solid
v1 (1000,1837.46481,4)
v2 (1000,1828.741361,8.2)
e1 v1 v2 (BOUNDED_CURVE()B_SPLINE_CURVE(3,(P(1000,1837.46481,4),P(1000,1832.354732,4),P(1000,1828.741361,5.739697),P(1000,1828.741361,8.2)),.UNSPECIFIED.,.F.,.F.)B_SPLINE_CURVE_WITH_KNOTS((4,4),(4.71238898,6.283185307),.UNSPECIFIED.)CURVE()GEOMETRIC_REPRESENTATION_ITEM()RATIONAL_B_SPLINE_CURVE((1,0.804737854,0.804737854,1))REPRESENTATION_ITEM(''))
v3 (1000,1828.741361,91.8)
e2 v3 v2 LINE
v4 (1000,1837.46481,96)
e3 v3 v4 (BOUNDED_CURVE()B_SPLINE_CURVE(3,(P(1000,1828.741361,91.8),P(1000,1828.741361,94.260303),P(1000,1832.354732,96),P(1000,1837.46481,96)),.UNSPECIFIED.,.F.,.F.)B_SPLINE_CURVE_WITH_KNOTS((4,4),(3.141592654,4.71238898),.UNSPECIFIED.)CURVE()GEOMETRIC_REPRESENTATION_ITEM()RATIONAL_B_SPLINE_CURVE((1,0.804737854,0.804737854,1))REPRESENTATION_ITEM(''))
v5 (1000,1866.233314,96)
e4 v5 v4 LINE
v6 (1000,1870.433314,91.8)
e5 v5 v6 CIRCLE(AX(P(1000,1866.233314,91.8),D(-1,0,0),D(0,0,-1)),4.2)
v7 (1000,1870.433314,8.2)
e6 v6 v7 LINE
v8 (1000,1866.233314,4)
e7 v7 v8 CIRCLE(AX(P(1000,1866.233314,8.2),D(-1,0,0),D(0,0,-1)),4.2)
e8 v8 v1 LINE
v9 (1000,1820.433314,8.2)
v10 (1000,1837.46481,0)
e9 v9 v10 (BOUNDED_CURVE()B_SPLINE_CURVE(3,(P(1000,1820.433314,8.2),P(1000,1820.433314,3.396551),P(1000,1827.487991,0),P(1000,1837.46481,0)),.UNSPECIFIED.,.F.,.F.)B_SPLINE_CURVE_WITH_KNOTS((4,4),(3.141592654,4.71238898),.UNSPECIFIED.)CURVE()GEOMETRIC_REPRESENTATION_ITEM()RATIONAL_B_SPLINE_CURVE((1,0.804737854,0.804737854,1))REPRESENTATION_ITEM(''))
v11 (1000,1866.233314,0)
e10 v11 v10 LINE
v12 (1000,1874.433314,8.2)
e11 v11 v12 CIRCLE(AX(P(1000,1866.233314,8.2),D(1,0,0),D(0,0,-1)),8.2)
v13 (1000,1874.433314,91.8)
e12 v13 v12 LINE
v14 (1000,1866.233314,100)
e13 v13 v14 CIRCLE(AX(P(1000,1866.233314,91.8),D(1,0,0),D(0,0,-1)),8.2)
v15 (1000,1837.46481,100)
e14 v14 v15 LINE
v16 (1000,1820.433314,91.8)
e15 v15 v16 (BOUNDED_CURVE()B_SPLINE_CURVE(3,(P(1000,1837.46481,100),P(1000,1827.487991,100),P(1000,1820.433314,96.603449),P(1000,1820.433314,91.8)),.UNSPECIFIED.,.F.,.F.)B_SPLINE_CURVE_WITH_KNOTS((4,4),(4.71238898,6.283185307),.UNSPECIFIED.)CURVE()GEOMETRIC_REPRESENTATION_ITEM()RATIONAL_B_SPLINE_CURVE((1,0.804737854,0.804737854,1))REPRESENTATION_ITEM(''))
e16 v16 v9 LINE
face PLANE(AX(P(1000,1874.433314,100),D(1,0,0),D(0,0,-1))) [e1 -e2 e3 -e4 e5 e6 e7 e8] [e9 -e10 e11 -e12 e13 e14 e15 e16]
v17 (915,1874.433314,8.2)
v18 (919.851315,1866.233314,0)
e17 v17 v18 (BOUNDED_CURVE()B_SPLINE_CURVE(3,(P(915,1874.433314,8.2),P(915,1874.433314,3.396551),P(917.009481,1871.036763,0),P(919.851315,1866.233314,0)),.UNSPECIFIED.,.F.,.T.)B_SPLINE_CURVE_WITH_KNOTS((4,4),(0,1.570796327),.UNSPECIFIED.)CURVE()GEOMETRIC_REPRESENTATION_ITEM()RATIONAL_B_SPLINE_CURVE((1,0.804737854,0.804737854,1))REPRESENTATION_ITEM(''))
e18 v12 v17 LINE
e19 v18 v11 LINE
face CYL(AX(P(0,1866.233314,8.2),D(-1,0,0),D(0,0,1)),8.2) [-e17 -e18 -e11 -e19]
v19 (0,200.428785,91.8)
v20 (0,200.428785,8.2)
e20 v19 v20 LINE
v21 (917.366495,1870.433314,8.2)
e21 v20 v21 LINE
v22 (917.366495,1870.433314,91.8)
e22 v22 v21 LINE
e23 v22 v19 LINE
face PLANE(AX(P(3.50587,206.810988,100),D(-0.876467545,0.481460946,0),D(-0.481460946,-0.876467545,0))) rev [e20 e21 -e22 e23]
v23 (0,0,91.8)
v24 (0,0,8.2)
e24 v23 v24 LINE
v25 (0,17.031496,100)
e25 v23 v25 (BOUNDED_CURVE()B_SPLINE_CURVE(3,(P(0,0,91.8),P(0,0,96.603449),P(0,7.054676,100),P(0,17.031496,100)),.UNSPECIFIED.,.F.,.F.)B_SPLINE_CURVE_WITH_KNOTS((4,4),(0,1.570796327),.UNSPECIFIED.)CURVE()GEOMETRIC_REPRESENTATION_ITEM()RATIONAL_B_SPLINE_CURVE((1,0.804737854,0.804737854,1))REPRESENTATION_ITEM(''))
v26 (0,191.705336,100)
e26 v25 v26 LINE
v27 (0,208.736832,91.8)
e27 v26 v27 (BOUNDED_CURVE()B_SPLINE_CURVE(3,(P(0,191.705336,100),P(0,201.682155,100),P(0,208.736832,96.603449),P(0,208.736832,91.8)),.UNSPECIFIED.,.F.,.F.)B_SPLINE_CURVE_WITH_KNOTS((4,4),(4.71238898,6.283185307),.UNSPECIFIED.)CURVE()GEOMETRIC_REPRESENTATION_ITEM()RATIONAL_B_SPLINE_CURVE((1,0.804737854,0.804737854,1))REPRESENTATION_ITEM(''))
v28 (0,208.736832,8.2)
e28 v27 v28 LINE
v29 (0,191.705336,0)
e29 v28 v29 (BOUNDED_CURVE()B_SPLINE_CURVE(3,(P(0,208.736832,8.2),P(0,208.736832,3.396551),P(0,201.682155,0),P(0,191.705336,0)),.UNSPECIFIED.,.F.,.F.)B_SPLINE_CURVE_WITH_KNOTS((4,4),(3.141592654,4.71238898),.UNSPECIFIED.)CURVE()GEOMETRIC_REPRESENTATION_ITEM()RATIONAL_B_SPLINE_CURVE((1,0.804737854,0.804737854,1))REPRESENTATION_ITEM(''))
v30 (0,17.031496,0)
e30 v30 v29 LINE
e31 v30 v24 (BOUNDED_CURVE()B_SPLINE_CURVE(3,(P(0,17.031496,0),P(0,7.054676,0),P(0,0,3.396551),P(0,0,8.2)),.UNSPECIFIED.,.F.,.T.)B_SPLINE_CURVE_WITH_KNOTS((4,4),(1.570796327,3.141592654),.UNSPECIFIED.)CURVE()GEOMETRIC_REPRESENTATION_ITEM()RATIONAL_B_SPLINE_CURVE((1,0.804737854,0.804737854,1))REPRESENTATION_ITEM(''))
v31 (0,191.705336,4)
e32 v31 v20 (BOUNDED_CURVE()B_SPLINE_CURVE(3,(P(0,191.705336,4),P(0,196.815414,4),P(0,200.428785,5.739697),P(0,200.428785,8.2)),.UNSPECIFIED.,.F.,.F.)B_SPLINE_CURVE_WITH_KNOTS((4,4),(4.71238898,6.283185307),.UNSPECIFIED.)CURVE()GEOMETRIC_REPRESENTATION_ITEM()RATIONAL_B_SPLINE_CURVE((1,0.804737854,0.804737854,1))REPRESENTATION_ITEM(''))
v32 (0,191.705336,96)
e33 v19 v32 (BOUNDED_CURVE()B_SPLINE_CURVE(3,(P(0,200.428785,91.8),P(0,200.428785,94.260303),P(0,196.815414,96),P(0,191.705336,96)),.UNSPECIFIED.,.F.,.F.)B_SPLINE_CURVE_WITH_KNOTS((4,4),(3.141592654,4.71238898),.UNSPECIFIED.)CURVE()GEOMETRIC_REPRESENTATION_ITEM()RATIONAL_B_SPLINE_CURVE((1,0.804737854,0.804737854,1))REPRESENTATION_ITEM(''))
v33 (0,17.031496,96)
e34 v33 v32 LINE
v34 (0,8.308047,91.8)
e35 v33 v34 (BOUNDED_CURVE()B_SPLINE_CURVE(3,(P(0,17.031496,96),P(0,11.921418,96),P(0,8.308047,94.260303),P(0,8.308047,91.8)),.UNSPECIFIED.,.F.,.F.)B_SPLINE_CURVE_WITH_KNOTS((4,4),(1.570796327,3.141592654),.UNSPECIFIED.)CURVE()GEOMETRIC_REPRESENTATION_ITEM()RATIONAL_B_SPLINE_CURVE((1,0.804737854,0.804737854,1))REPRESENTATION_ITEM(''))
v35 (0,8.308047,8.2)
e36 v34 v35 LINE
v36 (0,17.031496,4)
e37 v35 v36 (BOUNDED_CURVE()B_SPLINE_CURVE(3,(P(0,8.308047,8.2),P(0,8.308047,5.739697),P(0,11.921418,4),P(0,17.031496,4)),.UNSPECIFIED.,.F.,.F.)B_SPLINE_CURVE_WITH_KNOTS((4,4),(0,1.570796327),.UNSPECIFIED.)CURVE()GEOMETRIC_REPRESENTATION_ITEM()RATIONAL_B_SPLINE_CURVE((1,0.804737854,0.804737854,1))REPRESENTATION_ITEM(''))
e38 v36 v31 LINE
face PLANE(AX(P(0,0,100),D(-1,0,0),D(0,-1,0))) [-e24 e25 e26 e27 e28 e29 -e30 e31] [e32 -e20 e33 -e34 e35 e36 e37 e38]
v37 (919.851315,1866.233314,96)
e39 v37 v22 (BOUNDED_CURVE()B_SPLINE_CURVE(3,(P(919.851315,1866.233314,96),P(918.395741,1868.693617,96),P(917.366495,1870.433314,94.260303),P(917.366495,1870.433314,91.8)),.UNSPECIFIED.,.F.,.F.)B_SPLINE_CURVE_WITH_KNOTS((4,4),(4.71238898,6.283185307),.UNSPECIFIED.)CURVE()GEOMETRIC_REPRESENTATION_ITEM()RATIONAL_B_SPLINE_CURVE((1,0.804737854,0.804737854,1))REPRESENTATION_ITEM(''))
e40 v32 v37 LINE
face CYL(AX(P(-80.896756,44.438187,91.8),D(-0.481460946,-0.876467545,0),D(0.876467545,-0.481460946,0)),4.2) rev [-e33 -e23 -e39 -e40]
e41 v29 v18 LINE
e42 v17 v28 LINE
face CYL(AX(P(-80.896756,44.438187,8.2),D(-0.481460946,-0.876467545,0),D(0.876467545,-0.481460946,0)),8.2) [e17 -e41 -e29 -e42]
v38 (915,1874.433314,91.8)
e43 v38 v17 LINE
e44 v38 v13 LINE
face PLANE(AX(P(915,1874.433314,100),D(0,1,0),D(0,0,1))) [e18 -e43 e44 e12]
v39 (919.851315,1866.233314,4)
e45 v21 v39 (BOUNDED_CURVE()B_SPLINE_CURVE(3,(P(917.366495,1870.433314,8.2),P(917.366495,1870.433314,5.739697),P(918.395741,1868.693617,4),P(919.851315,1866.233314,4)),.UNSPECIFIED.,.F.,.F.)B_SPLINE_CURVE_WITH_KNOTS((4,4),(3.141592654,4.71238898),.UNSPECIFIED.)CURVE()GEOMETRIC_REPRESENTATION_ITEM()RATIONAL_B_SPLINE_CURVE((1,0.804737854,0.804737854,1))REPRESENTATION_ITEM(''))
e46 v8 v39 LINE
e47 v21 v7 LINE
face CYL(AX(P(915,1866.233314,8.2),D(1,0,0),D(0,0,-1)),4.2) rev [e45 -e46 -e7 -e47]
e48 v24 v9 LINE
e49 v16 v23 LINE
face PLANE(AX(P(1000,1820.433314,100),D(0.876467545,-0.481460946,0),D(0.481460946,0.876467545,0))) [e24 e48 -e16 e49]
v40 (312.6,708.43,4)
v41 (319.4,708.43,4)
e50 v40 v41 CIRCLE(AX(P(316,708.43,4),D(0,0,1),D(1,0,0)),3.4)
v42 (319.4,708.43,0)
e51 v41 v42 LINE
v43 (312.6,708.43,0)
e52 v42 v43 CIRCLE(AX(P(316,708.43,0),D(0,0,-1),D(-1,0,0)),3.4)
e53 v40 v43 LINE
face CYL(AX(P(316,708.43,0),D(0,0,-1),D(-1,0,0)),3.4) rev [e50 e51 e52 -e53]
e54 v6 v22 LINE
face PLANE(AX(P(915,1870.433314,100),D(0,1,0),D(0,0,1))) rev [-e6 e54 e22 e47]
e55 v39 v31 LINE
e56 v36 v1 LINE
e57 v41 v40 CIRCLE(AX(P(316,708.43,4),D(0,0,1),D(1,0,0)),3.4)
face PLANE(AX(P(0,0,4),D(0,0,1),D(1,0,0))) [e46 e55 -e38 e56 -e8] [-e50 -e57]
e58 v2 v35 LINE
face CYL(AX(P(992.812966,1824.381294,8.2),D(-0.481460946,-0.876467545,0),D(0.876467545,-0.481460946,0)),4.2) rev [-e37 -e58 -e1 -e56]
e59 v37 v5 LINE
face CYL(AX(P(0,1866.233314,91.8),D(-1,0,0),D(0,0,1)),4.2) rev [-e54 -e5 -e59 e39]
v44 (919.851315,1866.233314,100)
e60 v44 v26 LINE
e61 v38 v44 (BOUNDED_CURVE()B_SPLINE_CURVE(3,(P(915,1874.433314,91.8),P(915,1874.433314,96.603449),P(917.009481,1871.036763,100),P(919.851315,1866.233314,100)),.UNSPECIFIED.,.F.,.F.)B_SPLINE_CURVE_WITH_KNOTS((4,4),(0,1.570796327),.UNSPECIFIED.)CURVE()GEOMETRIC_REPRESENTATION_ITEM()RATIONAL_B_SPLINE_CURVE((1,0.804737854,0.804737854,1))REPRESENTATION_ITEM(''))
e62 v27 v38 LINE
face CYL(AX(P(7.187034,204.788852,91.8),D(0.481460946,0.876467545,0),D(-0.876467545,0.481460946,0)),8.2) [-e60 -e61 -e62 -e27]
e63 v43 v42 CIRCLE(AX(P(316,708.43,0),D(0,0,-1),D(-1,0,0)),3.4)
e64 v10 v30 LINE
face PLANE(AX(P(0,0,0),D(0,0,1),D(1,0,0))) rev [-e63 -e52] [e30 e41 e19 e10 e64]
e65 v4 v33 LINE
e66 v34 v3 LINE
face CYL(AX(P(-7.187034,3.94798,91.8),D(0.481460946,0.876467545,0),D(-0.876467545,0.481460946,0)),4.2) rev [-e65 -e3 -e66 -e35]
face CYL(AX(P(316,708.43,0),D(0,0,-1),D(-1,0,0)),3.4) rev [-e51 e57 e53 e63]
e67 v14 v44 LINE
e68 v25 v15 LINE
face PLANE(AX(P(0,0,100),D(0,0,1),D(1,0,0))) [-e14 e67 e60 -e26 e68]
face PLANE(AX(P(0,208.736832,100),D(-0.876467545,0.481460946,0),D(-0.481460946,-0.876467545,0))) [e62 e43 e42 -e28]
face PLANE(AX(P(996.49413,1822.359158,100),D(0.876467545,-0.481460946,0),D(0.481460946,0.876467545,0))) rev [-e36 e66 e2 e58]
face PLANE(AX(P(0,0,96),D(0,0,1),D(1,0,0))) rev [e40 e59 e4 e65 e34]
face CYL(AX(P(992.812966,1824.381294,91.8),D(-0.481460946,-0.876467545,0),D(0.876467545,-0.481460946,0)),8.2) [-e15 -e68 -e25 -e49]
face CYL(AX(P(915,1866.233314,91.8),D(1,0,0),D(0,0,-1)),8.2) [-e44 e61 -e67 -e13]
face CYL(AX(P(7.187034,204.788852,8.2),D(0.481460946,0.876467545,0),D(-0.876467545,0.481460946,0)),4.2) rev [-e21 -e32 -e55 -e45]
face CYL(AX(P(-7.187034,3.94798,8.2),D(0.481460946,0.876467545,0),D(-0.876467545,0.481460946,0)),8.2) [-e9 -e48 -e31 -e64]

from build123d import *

# Parameters (mm, degrees)
BOSS_EXTRUDE1_DEPTH   = 100
SHELL1_T              = -4
FILLET1_R             = 8.2
FILLET2_R             = 4.2
M8_TAPPED_HOLE1_D     = 6.8
M8_TAPPED_HOLE1_DEPTH = 19.75
M8_TAPPED_HOLE1_TIP   = 2.042926105


with BuildPart() as part:
    # Sketch1 → Boss-Extrude1 (new body)
    with BuildSketch(Plane.XY):
        Polygon((0, 0), (0, 208.736831721), (915, 1874.433314365), (1000, 1874.433314365), (1000, 1820.433314365), align=None)
    extrude(amount=BOSS_EXTRUDE1_DEPTH)

    # Shell1
    shell1_openings = [part.faces().sort_by_distance(p)[0] for p in [
        (0, 104.36841586, 50),
        (1000, 1847.433314365, 50),
    ]]
    offset(amount=SHELL1_T, openings=shell1_openings, kind=Kind.INTERSECTION)

    # Fillet1
    fillet1_edges = [part.edges().sort_by_distance(p)[0] for p in [
        (457.5, 1041.585073043, 100),
        (957.5, 1874.433314365, 100),
        (957.5, 1874.433314365, 0),
        (457.5, 1041.585073043, 0),
        (500, 910.216657182, 0),
        (500, 910.216657182, 100),
    ]]
    fillet(fillet1_edges, radius=FILLET1_R)

    # Fillet2
    fillet2_edges = [part.edges().sort_by_distance(p)[0] for p in [
        (958.683247588, 1870.433314365, 96),
        (458.683247588, 1035.431049715, 96),
        (500, 918.524703838, 96),
        (500, 918.524703838, 4),
        (458.683247588, 1035.431049715, 4),
        (958.683247588, 1870.433314365, 4),
    ]]
    fillet(fillet2_edges, radius=FILLET2_R)

    # M8 Tapped Hole1
    with Locations(Plane(origin=(0, 0, 0), x_dir=(-1, 0, 0), z_dir=(0, 0, -1))):
        with Locations((-316, 708.43)):
            Hole(M8_TAPPED_HOLE1_D / 2, depth=M8_TAPPED_HOLE1_DEPTH)
            with Locations((0, 0, -(M8_TAPPED_HOLE1_DEPTH + M8_TAPPED_HOLE1_TIP / 2))):  # 118° drill point
                Cone(0, M8_TAPPED_HOLE1_D / 2, M8_TAPPED_HOLE1_TIP, mode=Mode.SUBTRACT)


solid = part.part
